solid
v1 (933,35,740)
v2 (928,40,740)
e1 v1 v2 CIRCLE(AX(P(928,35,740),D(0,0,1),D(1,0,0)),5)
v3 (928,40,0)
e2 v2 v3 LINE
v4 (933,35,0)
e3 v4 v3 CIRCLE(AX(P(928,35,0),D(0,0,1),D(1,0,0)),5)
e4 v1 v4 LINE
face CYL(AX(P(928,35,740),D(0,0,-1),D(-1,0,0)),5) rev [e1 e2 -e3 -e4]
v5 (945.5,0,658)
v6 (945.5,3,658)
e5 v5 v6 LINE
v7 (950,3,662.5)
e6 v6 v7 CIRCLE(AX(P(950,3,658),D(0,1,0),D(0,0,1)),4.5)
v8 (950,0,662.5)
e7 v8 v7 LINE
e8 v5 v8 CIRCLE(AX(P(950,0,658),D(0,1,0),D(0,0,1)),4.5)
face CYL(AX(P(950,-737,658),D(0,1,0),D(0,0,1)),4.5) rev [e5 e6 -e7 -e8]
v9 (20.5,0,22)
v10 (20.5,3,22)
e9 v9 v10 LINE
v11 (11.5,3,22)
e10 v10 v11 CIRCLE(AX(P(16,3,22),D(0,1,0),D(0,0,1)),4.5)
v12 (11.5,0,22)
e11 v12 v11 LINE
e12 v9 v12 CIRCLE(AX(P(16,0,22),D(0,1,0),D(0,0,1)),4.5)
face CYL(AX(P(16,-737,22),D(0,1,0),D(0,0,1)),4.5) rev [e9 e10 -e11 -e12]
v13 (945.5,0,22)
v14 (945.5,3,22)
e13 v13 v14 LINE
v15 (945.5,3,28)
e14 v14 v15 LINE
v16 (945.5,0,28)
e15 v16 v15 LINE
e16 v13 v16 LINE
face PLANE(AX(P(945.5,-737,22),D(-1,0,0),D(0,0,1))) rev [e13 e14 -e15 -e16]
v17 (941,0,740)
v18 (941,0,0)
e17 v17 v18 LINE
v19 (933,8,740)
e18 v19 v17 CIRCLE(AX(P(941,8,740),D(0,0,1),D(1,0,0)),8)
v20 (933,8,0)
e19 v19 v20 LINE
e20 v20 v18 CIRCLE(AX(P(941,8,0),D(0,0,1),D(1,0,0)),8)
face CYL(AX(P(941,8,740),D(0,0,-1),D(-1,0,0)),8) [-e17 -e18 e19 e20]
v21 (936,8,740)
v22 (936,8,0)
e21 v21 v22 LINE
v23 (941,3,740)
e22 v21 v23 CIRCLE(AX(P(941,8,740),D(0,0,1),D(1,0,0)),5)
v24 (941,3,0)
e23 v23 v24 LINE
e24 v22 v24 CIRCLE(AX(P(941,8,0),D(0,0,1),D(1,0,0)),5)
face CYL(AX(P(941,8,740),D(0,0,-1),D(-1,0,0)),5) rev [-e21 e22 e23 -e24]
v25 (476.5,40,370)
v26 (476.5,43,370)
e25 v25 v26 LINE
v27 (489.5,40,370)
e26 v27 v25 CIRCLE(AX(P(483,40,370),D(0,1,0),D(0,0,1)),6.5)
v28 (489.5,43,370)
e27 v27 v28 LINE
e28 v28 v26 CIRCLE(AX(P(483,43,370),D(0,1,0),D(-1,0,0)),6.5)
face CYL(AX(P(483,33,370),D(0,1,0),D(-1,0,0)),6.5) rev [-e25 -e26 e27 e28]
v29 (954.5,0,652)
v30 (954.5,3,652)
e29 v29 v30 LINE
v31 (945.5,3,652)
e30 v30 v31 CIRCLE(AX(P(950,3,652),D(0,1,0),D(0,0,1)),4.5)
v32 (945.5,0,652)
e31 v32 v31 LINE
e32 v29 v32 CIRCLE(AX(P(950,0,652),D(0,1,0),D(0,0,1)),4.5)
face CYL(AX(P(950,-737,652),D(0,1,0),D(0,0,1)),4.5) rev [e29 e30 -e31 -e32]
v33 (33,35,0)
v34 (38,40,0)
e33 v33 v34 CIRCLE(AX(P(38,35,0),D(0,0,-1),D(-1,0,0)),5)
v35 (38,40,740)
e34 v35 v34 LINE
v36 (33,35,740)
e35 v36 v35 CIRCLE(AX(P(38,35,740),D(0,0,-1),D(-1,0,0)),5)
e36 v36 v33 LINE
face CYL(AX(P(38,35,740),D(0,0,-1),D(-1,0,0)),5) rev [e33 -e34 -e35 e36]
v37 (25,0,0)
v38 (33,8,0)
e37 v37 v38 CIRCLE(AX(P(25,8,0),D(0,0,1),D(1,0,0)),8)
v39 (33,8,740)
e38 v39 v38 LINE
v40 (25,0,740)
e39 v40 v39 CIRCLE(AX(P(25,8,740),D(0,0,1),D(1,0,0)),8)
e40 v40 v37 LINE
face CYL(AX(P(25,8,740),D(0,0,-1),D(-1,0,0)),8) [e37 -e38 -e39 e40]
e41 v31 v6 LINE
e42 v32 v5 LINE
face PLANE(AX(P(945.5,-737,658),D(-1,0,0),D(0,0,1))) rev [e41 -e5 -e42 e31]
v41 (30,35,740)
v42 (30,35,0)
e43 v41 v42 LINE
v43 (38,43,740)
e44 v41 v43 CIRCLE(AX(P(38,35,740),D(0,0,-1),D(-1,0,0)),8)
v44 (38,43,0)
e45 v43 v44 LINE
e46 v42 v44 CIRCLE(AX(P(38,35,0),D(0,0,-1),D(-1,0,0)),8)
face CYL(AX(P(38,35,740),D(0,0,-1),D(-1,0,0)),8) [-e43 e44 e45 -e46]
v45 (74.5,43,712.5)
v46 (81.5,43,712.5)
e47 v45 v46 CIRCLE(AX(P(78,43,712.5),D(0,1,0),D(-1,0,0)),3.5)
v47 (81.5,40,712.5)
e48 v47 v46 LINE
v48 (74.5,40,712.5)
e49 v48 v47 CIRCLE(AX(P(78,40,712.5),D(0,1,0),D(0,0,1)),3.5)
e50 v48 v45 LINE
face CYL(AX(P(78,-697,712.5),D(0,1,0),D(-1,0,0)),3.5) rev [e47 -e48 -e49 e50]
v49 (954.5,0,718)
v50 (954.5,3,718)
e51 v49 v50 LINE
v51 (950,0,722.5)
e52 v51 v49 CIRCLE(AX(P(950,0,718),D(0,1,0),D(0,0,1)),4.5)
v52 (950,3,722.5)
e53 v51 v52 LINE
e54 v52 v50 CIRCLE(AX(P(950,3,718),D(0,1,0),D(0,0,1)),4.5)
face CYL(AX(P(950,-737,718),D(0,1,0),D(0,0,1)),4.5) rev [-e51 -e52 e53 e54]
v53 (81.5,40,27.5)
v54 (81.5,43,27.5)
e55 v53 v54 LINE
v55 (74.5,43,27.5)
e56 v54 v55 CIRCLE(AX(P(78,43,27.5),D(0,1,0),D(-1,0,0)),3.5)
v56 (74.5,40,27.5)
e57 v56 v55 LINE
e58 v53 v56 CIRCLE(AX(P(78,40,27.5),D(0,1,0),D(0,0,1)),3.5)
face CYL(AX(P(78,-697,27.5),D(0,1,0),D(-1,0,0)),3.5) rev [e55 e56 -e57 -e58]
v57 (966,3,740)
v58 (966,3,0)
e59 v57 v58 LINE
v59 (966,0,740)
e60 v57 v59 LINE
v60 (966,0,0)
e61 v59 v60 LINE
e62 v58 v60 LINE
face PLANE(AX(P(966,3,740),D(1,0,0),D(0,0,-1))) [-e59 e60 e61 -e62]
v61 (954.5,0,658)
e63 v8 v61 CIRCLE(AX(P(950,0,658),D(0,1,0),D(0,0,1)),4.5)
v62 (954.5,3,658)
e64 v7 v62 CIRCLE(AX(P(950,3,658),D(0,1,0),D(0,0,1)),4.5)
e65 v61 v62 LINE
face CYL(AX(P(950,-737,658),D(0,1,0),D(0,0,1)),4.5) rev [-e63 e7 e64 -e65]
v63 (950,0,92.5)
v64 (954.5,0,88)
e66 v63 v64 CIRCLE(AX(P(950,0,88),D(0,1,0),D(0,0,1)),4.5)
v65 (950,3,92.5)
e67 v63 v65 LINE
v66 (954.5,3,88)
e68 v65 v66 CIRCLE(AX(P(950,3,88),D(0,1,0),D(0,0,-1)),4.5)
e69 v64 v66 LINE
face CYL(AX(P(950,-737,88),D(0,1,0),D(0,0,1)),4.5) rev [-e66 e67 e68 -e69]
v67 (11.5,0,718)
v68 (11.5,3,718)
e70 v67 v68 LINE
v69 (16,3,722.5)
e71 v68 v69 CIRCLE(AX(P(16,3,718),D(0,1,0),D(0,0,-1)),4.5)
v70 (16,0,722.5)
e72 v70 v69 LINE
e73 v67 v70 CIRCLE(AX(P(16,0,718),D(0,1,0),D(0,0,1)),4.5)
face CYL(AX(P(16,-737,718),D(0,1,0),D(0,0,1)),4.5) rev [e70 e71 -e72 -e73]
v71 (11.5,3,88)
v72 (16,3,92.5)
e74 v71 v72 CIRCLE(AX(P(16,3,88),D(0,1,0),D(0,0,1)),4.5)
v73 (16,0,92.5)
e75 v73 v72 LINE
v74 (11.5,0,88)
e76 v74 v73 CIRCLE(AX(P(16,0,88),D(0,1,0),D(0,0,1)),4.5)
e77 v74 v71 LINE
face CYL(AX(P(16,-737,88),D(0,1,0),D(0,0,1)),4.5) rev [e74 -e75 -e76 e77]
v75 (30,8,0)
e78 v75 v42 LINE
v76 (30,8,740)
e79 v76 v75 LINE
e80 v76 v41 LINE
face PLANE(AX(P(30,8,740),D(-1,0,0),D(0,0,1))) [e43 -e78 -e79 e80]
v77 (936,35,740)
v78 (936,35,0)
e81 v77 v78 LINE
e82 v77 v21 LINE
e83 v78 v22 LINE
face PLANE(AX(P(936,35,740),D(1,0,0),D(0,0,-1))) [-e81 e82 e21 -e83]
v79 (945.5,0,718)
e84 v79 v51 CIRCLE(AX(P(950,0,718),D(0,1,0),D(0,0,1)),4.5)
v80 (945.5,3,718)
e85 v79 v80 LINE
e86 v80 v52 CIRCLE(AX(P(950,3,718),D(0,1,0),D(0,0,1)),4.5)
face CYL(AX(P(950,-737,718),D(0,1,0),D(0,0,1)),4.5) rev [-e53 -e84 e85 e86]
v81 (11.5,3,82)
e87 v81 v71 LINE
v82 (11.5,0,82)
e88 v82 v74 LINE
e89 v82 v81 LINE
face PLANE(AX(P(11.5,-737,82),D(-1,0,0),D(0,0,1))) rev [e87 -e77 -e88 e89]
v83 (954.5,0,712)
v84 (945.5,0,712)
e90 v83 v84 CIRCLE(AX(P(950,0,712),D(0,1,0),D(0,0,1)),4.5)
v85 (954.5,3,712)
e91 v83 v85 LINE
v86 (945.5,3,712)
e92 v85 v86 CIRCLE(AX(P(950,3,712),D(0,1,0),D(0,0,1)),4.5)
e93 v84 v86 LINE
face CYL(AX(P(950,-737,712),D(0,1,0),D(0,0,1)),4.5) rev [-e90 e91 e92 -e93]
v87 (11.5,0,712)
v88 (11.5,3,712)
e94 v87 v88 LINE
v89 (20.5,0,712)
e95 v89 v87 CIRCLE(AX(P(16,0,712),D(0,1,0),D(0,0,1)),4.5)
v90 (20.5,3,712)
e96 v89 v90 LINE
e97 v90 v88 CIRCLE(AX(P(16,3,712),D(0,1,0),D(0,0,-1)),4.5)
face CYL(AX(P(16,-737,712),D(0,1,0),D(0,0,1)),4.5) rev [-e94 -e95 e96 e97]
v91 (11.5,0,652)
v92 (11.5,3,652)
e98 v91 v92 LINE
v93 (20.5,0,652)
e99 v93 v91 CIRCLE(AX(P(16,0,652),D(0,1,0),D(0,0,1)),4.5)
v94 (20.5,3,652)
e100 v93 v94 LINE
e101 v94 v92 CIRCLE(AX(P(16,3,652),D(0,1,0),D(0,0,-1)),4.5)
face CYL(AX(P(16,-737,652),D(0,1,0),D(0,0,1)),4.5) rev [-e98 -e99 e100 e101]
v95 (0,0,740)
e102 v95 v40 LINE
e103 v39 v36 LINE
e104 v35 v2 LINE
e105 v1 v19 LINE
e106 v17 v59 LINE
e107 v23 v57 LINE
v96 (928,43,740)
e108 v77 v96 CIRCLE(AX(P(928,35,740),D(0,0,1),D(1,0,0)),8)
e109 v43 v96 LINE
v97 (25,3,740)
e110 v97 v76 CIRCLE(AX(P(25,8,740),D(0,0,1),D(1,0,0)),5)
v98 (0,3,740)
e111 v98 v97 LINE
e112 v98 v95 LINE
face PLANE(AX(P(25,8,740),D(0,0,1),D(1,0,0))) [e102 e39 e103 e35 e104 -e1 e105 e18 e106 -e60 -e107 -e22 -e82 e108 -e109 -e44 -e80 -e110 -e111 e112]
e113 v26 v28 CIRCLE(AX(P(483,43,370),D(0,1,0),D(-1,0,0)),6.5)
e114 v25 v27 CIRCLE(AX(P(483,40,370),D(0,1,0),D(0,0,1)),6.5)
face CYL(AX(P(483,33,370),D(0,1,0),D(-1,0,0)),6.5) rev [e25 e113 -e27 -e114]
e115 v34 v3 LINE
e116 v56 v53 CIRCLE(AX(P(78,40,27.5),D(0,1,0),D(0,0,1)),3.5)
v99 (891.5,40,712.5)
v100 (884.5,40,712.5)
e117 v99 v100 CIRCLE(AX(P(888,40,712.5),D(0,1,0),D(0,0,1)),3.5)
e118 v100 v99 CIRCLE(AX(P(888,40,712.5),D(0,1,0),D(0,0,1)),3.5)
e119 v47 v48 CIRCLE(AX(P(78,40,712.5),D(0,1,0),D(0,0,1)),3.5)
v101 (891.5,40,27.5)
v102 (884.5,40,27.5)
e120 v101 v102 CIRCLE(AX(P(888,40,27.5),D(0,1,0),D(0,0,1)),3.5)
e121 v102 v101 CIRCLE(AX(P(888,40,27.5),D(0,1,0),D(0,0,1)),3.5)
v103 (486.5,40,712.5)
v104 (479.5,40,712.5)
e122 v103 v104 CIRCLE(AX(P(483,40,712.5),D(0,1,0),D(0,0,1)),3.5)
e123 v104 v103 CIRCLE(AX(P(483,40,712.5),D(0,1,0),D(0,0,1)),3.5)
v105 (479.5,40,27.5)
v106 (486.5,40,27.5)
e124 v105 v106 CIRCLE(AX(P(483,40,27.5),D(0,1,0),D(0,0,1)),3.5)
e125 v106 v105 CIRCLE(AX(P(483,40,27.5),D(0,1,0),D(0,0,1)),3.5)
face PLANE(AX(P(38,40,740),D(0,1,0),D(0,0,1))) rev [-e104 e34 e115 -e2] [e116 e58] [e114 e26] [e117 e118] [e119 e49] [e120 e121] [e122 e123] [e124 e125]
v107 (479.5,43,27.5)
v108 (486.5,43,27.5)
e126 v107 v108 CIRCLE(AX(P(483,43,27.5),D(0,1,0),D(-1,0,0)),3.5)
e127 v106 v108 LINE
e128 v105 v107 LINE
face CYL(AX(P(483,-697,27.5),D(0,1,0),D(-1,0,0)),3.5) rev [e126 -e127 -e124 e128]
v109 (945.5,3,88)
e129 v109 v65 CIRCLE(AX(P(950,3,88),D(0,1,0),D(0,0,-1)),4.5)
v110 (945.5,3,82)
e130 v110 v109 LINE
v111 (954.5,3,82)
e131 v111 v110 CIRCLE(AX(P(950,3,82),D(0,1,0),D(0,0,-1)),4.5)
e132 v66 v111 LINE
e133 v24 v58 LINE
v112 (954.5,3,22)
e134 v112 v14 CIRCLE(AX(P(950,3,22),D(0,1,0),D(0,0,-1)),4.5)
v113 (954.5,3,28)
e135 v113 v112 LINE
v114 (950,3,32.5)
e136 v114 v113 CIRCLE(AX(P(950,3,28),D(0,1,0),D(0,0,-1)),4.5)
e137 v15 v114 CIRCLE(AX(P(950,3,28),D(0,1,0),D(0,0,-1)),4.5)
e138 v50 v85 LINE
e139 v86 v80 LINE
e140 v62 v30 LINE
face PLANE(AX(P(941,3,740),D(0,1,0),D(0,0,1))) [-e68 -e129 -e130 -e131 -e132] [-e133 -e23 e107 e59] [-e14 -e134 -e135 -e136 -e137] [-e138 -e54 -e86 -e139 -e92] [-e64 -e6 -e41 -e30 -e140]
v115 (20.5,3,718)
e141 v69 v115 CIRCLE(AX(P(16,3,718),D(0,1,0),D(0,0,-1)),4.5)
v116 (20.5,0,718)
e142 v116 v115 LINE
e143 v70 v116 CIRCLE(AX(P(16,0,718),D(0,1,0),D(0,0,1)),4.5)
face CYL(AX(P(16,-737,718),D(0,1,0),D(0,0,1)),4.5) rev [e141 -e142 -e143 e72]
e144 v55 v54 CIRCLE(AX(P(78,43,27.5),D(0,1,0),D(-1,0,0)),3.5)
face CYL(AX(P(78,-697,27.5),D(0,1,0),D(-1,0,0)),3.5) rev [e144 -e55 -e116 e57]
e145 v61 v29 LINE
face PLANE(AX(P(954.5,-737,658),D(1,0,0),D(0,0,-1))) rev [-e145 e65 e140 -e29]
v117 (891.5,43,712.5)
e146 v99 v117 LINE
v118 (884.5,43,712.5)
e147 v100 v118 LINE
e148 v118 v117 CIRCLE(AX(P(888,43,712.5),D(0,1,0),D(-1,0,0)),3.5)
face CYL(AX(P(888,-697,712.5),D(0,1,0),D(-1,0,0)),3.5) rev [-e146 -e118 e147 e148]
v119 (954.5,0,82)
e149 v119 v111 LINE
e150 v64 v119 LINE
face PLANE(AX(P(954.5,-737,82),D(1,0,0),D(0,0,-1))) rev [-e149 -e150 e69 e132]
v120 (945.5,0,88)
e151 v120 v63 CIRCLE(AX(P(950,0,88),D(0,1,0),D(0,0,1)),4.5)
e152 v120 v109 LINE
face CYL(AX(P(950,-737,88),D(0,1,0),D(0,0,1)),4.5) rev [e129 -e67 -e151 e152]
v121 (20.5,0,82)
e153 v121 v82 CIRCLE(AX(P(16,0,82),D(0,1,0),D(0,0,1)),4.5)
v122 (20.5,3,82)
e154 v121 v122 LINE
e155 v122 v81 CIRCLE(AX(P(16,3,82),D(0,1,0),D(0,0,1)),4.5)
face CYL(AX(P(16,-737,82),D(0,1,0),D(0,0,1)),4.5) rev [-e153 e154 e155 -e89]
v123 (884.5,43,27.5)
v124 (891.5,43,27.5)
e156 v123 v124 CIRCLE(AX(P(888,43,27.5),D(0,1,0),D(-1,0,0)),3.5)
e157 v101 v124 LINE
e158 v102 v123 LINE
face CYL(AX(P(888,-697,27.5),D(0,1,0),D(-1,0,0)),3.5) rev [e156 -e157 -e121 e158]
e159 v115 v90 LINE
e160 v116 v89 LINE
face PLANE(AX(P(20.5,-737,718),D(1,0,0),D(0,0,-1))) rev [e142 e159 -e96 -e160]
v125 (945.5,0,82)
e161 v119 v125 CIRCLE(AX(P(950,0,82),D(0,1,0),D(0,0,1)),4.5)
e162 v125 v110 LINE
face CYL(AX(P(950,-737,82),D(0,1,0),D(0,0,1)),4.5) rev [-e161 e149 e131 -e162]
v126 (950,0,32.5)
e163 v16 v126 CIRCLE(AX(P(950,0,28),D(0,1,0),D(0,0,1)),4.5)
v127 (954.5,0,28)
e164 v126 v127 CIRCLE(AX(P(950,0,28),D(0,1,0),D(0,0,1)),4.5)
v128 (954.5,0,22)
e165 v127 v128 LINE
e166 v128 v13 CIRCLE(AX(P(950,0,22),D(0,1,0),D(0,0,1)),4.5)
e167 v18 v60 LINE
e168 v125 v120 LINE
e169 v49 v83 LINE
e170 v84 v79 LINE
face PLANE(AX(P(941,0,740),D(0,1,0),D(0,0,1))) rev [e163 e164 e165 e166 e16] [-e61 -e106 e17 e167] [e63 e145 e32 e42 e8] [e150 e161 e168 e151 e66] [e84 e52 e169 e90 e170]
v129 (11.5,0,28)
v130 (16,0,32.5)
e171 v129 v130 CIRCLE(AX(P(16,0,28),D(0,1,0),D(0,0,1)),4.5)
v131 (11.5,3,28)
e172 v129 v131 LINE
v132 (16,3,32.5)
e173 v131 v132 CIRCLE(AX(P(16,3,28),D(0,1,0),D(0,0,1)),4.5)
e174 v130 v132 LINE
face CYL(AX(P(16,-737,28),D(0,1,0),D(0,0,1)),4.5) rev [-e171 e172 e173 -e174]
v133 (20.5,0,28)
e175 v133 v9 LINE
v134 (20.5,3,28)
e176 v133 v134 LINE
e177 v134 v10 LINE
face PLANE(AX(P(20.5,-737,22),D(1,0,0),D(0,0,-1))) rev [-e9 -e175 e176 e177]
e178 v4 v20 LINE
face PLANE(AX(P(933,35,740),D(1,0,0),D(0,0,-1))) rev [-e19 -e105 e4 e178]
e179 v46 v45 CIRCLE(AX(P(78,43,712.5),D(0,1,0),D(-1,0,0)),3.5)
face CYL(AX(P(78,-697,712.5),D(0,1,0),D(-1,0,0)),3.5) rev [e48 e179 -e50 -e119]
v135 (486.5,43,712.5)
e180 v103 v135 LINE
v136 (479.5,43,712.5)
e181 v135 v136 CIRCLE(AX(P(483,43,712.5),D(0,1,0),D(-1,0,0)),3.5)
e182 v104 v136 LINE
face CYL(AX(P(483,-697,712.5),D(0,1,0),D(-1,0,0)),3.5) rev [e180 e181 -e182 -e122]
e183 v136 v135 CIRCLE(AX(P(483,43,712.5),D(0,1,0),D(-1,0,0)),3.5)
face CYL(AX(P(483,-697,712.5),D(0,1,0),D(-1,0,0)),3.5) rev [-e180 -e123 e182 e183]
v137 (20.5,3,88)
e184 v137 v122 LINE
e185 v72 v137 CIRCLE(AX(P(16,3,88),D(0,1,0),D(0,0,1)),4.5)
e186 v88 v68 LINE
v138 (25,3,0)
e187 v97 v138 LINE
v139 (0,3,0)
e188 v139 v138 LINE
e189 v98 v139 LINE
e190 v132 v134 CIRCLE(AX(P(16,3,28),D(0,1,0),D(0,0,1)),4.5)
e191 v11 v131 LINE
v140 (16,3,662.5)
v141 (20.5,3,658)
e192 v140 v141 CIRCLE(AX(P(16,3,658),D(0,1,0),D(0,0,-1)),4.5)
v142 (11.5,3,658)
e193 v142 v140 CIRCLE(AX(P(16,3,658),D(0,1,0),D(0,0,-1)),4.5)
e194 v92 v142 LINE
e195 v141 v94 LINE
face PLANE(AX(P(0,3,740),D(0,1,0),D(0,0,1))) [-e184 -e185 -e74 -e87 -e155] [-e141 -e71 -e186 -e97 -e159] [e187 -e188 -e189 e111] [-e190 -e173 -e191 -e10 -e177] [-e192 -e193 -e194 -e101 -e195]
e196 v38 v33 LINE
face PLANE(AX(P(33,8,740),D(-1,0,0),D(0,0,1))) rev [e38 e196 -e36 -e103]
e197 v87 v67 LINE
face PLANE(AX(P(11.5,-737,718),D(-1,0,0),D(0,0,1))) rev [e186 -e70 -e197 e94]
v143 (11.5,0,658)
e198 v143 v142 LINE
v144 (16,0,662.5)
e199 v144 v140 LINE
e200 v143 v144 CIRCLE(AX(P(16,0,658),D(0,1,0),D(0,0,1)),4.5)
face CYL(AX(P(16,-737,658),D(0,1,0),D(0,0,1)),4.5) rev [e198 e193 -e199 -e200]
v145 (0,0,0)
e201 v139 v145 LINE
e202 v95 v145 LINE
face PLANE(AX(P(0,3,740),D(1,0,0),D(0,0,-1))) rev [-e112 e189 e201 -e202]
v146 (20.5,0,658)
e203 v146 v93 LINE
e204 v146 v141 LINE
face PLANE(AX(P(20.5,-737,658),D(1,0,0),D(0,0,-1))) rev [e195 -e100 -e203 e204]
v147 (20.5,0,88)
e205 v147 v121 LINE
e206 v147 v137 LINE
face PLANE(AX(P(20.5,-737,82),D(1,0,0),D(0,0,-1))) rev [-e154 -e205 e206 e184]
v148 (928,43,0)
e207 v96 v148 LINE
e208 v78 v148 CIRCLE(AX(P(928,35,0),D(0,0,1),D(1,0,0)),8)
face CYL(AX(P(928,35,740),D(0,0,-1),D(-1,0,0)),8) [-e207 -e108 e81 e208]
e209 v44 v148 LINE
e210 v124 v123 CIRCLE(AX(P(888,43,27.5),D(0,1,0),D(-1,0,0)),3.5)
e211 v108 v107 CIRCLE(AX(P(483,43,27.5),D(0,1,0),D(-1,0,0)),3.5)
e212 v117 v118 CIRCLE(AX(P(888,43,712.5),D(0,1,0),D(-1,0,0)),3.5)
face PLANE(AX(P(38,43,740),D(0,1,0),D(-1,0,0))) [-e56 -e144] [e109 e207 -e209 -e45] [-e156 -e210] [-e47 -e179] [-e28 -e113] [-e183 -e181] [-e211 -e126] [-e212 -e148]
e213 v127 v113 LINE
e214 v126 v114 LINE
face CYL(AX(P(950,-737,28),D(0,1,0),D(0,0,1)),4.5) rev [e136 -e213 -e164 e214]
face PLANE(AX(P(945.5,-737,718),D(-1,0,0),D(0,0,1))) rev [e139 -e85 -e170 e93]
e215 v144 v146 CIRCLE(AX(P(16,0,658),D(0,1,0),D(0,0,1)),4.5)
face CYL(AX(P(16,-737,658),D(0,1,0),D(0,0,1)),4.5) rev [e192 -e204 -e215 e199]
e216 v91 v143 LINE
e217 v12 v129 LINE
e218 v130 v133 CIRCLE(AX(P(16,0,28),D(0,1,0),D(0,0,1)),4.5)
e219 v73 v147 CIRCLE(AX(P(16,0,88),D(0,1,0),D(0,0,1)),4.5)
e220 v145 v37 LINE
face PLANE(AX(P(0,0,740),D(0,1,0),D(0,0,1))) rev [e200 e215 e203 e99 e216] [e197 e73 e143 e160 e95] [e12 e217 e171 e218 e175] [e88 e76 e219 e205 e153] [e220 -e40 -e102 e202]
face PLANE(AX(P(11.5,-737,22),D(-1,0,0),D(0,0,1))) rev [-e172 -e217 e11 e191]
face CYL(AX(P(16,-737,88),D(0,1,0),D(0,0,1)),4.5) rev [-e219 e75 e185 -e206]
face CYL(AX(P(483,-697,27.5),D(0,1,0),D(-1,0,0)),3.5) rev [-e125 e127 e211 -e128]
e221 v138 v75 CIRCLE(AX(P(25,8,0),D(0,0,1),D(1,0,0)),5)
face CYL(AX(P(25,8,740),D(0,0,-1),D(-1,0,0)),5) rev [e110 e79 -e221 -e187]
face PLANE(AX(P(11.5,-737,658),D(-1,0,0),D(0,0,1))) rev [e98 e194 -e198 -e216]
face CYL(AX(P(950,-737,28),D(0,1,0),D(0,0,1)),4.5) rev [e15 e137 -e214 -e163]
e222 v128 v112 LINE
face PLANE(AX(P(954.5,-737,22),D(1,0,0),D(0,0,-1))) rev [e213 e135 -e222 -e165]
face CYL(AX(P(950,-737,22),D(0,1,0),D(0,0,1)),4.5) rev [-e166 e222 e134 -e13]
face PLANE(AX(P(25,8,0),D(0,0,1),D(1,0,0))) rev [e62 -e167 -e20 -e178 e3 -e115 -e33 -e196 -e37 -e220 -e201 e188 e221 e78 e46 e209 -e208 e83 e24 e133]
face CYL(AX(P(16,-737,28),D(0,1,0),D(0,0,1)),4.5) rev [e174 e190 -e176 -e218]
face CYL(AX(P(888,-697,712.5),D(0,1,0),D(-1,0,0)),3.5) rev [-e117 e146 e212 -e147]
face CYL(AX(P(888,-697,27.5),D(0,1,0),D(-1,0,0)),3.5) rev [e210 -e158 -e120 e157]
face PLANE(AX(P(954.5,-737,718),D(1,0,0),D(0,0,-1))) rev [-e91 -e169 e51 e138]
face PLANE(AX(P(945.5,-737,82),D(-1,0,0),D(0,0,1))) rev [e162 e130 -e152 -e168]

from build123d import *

# Parameters (mm, degrees)
EXTRUDE_1_DEPTH     = 740
SKETCH_2_R          = 3.5
CUT_EXTRUDE_1_DEPTH = 740
CUT_EXTRUDE_2_DEPTH = 740
SKETCH_4_R          = 6.5
CUT_EXTRUDE_3_DEPTH = 10


with BuildPart() as part:
    # 草图1 → 凸台-拉伸1 (new body)
    with BuildSketch(Plane.XY):
        with BuildLine():
            Line((0, 0), (25, 0))
            ThreePointArc((25, 0), (30.656854249, 2.343145751), (33, 8))
            Line((33, 8), (33, 35))
            ThreePointArc((33, 35), (34.464466094, 38.535533906), (38, 40))
            Line((38, 40), (928, 40))
            ThreePointArc((928, 40), (931.535533906, 38.535533906), (933, 35))
            Line((933, 35), (933, 8))
            ThreePointArc((933, 8), (935.343145751, 2.343145751), (941, 0))
            Line((941, 0), (966, 0))
            Line((966, 0), (966, 3))
            Line((966, 3), (941, 3))
            ThreePointArc((941, 3), (937.464466094, 4.464466094), (936, 8))
            Line((936, 8), (936, 35))
            ThreePointArc((936, 35), (933.656854249, 40.656854249), (928, 43))
            Line((928, 43), (38, 43))
            ThreePointArc((38, 43), (32.343145751, 40.656854249), (30, 35))
            Line((30, 35), (30, 8))
            ThreePointArc((30, 8), (28.535533906, 4.464466094), (25, 3))
            Line((25, 3), (0, 3))
            Line((0, 3), (0, 0))
        make_face()
    extrude(amount=EXTRUDE_1_DEPTH)

    # 草图2 → 切除-拉伸1 (cut)
    with BuildSketch(Plane(origin=(0, 43, 0), x_dir=(1, 0, 0), z_dir=(0, 1, 0))):
        with Locations(Location((78, -27.5, 0), (0, 0, 180))):
            Circle(SKETCH_2_R)
        with Locations(Location((483, -27.5, 0), (0, 0, 180))):
            Circle(SKETCH_2_R)
        with Locations(Location((888, -27.5, 0), (0, 0, 180))):
            Circle(SKETCH_2_R)
        with Locations(Location((78, -712.5, 0), (0, 0, 180))):
            Circle(SKETCH_2_R)
        with Locations(Location((888, -712.5, 0), (0, 0, 180))):
            Circle(SKETCH_2_R)
        with Locations(Location((483, -712.5, 0), (0, 0, 180))):
            Circle(SKETCH_2_R)
    extrude(amount=-CUT_EXTRUDE_1_DEPTH, mode=Mode.SUBTRACT)

    # 草图3 → 切除-拉伸2 (cut)
    with BuildSketch(Plane(origin=(0, 3, 0), x_dir=(1, 0, 0), z_dir=(0, 1, 0))):
        with BuildLine():
            Line((20.5, -22), (20.5, -28))
            ThreePointArc((20.5, -28), (16, -32.5), (11.5, -28))
            Line((11.5, -28), (11.5, -22))
            ThreePointArc((11.5, -22), (16, -17.5), (20.5, -22))
        make_face()
        with BuildLine():
            Line((20.5, -82), (20.5, -88))
            ThreePointArc((20.5, -88), (16, -92.5), (11.5, -88))
            Line((11.5, -88), (11.5, -82))
            ThreePointArc((11.5, -82), (16, -77.5), (20.5, -82))
        make_face()
        with BuildLine():
            Line((945.5, -82), (945.5, -88))
            ThreePointArc((945.5, -88), (950, -92.5), (954.5, -88))
            Line((954.5, -88), (954.5, -82))
            ThreePointArc((954.5, -82), (950, -77.5), (945.5, -82))
        make_face()
        with BuildLine():
            Line((945.5, -22), (945.5, -28))
            ThreePointArc((945.5, -28), (950, -32.5), (954.5, -28))
            Line((954.5, -28), (954.5, -22))
            ThreePointArc((954.5, -22), (950, -17.5), (945.5, -22))
        make_face()
        with BuildLine():
            Line((945.5, -658), (945.5, -652))
            ThreePointArc((945.5, -652), (950, -647.5), (954.5, -652))
            Line((954.5, -652), (954.5, -658))
            ThreePointArc((954.5, -658), (950, -662.5), (945.5, -658))
        make_face()
        with BuildLine():
            Line((945.5, -718), (945.5, -712))
            ThreePointArc((945.5, -712), (950, -707.5), (954.5, -712))
            Line((954.5, -712), (954.5, -718))
            ThreePointArc((954.5, -718), (950, -722.5), (945.5, -718))
        make_face()
        with BuildLine():
            Line((20.5, -658), (20.5, -652))
            ThreePointArc((20.5, -652), (16, -647.5), (11.5, -652))
            Line((11.5, -652), (11.5, -658))
            ThreePointArc((11.5, -658), (16, -662.5), (20.5, -658))
        make_face()
        with BuildLine():
            Line((20.5, -718), (20.5, -712))
            ThreePointArc((20.5, -712), (16, -707.5), (11.5, -712))
            Line((11.5, -712), (11.5, -718))
            ThreePointArc((11.5, -718), (16, -722.5), (20.5, -718))
        make_face()
    extrude(amount=-CUT_EXTRUDE_2_DEPTH, mode=Mode.SUBTRACT)

    # 草图4 → 切除-拉伸3 (cut)
    with BuildSketch(Plane(origin=(0, 43, 0), x_dir=(1, 0, 0), z_dir=(0, 1, 0))):
        with Locations(Location((483, -370, 0), (0, 0, 180))):
            Circle(SKETCH_4_R)
    extrude(amount=-CUT_EXTRUDE_3_DEPTH, mode=Mode.SUBTRACT)


solid = part.part
